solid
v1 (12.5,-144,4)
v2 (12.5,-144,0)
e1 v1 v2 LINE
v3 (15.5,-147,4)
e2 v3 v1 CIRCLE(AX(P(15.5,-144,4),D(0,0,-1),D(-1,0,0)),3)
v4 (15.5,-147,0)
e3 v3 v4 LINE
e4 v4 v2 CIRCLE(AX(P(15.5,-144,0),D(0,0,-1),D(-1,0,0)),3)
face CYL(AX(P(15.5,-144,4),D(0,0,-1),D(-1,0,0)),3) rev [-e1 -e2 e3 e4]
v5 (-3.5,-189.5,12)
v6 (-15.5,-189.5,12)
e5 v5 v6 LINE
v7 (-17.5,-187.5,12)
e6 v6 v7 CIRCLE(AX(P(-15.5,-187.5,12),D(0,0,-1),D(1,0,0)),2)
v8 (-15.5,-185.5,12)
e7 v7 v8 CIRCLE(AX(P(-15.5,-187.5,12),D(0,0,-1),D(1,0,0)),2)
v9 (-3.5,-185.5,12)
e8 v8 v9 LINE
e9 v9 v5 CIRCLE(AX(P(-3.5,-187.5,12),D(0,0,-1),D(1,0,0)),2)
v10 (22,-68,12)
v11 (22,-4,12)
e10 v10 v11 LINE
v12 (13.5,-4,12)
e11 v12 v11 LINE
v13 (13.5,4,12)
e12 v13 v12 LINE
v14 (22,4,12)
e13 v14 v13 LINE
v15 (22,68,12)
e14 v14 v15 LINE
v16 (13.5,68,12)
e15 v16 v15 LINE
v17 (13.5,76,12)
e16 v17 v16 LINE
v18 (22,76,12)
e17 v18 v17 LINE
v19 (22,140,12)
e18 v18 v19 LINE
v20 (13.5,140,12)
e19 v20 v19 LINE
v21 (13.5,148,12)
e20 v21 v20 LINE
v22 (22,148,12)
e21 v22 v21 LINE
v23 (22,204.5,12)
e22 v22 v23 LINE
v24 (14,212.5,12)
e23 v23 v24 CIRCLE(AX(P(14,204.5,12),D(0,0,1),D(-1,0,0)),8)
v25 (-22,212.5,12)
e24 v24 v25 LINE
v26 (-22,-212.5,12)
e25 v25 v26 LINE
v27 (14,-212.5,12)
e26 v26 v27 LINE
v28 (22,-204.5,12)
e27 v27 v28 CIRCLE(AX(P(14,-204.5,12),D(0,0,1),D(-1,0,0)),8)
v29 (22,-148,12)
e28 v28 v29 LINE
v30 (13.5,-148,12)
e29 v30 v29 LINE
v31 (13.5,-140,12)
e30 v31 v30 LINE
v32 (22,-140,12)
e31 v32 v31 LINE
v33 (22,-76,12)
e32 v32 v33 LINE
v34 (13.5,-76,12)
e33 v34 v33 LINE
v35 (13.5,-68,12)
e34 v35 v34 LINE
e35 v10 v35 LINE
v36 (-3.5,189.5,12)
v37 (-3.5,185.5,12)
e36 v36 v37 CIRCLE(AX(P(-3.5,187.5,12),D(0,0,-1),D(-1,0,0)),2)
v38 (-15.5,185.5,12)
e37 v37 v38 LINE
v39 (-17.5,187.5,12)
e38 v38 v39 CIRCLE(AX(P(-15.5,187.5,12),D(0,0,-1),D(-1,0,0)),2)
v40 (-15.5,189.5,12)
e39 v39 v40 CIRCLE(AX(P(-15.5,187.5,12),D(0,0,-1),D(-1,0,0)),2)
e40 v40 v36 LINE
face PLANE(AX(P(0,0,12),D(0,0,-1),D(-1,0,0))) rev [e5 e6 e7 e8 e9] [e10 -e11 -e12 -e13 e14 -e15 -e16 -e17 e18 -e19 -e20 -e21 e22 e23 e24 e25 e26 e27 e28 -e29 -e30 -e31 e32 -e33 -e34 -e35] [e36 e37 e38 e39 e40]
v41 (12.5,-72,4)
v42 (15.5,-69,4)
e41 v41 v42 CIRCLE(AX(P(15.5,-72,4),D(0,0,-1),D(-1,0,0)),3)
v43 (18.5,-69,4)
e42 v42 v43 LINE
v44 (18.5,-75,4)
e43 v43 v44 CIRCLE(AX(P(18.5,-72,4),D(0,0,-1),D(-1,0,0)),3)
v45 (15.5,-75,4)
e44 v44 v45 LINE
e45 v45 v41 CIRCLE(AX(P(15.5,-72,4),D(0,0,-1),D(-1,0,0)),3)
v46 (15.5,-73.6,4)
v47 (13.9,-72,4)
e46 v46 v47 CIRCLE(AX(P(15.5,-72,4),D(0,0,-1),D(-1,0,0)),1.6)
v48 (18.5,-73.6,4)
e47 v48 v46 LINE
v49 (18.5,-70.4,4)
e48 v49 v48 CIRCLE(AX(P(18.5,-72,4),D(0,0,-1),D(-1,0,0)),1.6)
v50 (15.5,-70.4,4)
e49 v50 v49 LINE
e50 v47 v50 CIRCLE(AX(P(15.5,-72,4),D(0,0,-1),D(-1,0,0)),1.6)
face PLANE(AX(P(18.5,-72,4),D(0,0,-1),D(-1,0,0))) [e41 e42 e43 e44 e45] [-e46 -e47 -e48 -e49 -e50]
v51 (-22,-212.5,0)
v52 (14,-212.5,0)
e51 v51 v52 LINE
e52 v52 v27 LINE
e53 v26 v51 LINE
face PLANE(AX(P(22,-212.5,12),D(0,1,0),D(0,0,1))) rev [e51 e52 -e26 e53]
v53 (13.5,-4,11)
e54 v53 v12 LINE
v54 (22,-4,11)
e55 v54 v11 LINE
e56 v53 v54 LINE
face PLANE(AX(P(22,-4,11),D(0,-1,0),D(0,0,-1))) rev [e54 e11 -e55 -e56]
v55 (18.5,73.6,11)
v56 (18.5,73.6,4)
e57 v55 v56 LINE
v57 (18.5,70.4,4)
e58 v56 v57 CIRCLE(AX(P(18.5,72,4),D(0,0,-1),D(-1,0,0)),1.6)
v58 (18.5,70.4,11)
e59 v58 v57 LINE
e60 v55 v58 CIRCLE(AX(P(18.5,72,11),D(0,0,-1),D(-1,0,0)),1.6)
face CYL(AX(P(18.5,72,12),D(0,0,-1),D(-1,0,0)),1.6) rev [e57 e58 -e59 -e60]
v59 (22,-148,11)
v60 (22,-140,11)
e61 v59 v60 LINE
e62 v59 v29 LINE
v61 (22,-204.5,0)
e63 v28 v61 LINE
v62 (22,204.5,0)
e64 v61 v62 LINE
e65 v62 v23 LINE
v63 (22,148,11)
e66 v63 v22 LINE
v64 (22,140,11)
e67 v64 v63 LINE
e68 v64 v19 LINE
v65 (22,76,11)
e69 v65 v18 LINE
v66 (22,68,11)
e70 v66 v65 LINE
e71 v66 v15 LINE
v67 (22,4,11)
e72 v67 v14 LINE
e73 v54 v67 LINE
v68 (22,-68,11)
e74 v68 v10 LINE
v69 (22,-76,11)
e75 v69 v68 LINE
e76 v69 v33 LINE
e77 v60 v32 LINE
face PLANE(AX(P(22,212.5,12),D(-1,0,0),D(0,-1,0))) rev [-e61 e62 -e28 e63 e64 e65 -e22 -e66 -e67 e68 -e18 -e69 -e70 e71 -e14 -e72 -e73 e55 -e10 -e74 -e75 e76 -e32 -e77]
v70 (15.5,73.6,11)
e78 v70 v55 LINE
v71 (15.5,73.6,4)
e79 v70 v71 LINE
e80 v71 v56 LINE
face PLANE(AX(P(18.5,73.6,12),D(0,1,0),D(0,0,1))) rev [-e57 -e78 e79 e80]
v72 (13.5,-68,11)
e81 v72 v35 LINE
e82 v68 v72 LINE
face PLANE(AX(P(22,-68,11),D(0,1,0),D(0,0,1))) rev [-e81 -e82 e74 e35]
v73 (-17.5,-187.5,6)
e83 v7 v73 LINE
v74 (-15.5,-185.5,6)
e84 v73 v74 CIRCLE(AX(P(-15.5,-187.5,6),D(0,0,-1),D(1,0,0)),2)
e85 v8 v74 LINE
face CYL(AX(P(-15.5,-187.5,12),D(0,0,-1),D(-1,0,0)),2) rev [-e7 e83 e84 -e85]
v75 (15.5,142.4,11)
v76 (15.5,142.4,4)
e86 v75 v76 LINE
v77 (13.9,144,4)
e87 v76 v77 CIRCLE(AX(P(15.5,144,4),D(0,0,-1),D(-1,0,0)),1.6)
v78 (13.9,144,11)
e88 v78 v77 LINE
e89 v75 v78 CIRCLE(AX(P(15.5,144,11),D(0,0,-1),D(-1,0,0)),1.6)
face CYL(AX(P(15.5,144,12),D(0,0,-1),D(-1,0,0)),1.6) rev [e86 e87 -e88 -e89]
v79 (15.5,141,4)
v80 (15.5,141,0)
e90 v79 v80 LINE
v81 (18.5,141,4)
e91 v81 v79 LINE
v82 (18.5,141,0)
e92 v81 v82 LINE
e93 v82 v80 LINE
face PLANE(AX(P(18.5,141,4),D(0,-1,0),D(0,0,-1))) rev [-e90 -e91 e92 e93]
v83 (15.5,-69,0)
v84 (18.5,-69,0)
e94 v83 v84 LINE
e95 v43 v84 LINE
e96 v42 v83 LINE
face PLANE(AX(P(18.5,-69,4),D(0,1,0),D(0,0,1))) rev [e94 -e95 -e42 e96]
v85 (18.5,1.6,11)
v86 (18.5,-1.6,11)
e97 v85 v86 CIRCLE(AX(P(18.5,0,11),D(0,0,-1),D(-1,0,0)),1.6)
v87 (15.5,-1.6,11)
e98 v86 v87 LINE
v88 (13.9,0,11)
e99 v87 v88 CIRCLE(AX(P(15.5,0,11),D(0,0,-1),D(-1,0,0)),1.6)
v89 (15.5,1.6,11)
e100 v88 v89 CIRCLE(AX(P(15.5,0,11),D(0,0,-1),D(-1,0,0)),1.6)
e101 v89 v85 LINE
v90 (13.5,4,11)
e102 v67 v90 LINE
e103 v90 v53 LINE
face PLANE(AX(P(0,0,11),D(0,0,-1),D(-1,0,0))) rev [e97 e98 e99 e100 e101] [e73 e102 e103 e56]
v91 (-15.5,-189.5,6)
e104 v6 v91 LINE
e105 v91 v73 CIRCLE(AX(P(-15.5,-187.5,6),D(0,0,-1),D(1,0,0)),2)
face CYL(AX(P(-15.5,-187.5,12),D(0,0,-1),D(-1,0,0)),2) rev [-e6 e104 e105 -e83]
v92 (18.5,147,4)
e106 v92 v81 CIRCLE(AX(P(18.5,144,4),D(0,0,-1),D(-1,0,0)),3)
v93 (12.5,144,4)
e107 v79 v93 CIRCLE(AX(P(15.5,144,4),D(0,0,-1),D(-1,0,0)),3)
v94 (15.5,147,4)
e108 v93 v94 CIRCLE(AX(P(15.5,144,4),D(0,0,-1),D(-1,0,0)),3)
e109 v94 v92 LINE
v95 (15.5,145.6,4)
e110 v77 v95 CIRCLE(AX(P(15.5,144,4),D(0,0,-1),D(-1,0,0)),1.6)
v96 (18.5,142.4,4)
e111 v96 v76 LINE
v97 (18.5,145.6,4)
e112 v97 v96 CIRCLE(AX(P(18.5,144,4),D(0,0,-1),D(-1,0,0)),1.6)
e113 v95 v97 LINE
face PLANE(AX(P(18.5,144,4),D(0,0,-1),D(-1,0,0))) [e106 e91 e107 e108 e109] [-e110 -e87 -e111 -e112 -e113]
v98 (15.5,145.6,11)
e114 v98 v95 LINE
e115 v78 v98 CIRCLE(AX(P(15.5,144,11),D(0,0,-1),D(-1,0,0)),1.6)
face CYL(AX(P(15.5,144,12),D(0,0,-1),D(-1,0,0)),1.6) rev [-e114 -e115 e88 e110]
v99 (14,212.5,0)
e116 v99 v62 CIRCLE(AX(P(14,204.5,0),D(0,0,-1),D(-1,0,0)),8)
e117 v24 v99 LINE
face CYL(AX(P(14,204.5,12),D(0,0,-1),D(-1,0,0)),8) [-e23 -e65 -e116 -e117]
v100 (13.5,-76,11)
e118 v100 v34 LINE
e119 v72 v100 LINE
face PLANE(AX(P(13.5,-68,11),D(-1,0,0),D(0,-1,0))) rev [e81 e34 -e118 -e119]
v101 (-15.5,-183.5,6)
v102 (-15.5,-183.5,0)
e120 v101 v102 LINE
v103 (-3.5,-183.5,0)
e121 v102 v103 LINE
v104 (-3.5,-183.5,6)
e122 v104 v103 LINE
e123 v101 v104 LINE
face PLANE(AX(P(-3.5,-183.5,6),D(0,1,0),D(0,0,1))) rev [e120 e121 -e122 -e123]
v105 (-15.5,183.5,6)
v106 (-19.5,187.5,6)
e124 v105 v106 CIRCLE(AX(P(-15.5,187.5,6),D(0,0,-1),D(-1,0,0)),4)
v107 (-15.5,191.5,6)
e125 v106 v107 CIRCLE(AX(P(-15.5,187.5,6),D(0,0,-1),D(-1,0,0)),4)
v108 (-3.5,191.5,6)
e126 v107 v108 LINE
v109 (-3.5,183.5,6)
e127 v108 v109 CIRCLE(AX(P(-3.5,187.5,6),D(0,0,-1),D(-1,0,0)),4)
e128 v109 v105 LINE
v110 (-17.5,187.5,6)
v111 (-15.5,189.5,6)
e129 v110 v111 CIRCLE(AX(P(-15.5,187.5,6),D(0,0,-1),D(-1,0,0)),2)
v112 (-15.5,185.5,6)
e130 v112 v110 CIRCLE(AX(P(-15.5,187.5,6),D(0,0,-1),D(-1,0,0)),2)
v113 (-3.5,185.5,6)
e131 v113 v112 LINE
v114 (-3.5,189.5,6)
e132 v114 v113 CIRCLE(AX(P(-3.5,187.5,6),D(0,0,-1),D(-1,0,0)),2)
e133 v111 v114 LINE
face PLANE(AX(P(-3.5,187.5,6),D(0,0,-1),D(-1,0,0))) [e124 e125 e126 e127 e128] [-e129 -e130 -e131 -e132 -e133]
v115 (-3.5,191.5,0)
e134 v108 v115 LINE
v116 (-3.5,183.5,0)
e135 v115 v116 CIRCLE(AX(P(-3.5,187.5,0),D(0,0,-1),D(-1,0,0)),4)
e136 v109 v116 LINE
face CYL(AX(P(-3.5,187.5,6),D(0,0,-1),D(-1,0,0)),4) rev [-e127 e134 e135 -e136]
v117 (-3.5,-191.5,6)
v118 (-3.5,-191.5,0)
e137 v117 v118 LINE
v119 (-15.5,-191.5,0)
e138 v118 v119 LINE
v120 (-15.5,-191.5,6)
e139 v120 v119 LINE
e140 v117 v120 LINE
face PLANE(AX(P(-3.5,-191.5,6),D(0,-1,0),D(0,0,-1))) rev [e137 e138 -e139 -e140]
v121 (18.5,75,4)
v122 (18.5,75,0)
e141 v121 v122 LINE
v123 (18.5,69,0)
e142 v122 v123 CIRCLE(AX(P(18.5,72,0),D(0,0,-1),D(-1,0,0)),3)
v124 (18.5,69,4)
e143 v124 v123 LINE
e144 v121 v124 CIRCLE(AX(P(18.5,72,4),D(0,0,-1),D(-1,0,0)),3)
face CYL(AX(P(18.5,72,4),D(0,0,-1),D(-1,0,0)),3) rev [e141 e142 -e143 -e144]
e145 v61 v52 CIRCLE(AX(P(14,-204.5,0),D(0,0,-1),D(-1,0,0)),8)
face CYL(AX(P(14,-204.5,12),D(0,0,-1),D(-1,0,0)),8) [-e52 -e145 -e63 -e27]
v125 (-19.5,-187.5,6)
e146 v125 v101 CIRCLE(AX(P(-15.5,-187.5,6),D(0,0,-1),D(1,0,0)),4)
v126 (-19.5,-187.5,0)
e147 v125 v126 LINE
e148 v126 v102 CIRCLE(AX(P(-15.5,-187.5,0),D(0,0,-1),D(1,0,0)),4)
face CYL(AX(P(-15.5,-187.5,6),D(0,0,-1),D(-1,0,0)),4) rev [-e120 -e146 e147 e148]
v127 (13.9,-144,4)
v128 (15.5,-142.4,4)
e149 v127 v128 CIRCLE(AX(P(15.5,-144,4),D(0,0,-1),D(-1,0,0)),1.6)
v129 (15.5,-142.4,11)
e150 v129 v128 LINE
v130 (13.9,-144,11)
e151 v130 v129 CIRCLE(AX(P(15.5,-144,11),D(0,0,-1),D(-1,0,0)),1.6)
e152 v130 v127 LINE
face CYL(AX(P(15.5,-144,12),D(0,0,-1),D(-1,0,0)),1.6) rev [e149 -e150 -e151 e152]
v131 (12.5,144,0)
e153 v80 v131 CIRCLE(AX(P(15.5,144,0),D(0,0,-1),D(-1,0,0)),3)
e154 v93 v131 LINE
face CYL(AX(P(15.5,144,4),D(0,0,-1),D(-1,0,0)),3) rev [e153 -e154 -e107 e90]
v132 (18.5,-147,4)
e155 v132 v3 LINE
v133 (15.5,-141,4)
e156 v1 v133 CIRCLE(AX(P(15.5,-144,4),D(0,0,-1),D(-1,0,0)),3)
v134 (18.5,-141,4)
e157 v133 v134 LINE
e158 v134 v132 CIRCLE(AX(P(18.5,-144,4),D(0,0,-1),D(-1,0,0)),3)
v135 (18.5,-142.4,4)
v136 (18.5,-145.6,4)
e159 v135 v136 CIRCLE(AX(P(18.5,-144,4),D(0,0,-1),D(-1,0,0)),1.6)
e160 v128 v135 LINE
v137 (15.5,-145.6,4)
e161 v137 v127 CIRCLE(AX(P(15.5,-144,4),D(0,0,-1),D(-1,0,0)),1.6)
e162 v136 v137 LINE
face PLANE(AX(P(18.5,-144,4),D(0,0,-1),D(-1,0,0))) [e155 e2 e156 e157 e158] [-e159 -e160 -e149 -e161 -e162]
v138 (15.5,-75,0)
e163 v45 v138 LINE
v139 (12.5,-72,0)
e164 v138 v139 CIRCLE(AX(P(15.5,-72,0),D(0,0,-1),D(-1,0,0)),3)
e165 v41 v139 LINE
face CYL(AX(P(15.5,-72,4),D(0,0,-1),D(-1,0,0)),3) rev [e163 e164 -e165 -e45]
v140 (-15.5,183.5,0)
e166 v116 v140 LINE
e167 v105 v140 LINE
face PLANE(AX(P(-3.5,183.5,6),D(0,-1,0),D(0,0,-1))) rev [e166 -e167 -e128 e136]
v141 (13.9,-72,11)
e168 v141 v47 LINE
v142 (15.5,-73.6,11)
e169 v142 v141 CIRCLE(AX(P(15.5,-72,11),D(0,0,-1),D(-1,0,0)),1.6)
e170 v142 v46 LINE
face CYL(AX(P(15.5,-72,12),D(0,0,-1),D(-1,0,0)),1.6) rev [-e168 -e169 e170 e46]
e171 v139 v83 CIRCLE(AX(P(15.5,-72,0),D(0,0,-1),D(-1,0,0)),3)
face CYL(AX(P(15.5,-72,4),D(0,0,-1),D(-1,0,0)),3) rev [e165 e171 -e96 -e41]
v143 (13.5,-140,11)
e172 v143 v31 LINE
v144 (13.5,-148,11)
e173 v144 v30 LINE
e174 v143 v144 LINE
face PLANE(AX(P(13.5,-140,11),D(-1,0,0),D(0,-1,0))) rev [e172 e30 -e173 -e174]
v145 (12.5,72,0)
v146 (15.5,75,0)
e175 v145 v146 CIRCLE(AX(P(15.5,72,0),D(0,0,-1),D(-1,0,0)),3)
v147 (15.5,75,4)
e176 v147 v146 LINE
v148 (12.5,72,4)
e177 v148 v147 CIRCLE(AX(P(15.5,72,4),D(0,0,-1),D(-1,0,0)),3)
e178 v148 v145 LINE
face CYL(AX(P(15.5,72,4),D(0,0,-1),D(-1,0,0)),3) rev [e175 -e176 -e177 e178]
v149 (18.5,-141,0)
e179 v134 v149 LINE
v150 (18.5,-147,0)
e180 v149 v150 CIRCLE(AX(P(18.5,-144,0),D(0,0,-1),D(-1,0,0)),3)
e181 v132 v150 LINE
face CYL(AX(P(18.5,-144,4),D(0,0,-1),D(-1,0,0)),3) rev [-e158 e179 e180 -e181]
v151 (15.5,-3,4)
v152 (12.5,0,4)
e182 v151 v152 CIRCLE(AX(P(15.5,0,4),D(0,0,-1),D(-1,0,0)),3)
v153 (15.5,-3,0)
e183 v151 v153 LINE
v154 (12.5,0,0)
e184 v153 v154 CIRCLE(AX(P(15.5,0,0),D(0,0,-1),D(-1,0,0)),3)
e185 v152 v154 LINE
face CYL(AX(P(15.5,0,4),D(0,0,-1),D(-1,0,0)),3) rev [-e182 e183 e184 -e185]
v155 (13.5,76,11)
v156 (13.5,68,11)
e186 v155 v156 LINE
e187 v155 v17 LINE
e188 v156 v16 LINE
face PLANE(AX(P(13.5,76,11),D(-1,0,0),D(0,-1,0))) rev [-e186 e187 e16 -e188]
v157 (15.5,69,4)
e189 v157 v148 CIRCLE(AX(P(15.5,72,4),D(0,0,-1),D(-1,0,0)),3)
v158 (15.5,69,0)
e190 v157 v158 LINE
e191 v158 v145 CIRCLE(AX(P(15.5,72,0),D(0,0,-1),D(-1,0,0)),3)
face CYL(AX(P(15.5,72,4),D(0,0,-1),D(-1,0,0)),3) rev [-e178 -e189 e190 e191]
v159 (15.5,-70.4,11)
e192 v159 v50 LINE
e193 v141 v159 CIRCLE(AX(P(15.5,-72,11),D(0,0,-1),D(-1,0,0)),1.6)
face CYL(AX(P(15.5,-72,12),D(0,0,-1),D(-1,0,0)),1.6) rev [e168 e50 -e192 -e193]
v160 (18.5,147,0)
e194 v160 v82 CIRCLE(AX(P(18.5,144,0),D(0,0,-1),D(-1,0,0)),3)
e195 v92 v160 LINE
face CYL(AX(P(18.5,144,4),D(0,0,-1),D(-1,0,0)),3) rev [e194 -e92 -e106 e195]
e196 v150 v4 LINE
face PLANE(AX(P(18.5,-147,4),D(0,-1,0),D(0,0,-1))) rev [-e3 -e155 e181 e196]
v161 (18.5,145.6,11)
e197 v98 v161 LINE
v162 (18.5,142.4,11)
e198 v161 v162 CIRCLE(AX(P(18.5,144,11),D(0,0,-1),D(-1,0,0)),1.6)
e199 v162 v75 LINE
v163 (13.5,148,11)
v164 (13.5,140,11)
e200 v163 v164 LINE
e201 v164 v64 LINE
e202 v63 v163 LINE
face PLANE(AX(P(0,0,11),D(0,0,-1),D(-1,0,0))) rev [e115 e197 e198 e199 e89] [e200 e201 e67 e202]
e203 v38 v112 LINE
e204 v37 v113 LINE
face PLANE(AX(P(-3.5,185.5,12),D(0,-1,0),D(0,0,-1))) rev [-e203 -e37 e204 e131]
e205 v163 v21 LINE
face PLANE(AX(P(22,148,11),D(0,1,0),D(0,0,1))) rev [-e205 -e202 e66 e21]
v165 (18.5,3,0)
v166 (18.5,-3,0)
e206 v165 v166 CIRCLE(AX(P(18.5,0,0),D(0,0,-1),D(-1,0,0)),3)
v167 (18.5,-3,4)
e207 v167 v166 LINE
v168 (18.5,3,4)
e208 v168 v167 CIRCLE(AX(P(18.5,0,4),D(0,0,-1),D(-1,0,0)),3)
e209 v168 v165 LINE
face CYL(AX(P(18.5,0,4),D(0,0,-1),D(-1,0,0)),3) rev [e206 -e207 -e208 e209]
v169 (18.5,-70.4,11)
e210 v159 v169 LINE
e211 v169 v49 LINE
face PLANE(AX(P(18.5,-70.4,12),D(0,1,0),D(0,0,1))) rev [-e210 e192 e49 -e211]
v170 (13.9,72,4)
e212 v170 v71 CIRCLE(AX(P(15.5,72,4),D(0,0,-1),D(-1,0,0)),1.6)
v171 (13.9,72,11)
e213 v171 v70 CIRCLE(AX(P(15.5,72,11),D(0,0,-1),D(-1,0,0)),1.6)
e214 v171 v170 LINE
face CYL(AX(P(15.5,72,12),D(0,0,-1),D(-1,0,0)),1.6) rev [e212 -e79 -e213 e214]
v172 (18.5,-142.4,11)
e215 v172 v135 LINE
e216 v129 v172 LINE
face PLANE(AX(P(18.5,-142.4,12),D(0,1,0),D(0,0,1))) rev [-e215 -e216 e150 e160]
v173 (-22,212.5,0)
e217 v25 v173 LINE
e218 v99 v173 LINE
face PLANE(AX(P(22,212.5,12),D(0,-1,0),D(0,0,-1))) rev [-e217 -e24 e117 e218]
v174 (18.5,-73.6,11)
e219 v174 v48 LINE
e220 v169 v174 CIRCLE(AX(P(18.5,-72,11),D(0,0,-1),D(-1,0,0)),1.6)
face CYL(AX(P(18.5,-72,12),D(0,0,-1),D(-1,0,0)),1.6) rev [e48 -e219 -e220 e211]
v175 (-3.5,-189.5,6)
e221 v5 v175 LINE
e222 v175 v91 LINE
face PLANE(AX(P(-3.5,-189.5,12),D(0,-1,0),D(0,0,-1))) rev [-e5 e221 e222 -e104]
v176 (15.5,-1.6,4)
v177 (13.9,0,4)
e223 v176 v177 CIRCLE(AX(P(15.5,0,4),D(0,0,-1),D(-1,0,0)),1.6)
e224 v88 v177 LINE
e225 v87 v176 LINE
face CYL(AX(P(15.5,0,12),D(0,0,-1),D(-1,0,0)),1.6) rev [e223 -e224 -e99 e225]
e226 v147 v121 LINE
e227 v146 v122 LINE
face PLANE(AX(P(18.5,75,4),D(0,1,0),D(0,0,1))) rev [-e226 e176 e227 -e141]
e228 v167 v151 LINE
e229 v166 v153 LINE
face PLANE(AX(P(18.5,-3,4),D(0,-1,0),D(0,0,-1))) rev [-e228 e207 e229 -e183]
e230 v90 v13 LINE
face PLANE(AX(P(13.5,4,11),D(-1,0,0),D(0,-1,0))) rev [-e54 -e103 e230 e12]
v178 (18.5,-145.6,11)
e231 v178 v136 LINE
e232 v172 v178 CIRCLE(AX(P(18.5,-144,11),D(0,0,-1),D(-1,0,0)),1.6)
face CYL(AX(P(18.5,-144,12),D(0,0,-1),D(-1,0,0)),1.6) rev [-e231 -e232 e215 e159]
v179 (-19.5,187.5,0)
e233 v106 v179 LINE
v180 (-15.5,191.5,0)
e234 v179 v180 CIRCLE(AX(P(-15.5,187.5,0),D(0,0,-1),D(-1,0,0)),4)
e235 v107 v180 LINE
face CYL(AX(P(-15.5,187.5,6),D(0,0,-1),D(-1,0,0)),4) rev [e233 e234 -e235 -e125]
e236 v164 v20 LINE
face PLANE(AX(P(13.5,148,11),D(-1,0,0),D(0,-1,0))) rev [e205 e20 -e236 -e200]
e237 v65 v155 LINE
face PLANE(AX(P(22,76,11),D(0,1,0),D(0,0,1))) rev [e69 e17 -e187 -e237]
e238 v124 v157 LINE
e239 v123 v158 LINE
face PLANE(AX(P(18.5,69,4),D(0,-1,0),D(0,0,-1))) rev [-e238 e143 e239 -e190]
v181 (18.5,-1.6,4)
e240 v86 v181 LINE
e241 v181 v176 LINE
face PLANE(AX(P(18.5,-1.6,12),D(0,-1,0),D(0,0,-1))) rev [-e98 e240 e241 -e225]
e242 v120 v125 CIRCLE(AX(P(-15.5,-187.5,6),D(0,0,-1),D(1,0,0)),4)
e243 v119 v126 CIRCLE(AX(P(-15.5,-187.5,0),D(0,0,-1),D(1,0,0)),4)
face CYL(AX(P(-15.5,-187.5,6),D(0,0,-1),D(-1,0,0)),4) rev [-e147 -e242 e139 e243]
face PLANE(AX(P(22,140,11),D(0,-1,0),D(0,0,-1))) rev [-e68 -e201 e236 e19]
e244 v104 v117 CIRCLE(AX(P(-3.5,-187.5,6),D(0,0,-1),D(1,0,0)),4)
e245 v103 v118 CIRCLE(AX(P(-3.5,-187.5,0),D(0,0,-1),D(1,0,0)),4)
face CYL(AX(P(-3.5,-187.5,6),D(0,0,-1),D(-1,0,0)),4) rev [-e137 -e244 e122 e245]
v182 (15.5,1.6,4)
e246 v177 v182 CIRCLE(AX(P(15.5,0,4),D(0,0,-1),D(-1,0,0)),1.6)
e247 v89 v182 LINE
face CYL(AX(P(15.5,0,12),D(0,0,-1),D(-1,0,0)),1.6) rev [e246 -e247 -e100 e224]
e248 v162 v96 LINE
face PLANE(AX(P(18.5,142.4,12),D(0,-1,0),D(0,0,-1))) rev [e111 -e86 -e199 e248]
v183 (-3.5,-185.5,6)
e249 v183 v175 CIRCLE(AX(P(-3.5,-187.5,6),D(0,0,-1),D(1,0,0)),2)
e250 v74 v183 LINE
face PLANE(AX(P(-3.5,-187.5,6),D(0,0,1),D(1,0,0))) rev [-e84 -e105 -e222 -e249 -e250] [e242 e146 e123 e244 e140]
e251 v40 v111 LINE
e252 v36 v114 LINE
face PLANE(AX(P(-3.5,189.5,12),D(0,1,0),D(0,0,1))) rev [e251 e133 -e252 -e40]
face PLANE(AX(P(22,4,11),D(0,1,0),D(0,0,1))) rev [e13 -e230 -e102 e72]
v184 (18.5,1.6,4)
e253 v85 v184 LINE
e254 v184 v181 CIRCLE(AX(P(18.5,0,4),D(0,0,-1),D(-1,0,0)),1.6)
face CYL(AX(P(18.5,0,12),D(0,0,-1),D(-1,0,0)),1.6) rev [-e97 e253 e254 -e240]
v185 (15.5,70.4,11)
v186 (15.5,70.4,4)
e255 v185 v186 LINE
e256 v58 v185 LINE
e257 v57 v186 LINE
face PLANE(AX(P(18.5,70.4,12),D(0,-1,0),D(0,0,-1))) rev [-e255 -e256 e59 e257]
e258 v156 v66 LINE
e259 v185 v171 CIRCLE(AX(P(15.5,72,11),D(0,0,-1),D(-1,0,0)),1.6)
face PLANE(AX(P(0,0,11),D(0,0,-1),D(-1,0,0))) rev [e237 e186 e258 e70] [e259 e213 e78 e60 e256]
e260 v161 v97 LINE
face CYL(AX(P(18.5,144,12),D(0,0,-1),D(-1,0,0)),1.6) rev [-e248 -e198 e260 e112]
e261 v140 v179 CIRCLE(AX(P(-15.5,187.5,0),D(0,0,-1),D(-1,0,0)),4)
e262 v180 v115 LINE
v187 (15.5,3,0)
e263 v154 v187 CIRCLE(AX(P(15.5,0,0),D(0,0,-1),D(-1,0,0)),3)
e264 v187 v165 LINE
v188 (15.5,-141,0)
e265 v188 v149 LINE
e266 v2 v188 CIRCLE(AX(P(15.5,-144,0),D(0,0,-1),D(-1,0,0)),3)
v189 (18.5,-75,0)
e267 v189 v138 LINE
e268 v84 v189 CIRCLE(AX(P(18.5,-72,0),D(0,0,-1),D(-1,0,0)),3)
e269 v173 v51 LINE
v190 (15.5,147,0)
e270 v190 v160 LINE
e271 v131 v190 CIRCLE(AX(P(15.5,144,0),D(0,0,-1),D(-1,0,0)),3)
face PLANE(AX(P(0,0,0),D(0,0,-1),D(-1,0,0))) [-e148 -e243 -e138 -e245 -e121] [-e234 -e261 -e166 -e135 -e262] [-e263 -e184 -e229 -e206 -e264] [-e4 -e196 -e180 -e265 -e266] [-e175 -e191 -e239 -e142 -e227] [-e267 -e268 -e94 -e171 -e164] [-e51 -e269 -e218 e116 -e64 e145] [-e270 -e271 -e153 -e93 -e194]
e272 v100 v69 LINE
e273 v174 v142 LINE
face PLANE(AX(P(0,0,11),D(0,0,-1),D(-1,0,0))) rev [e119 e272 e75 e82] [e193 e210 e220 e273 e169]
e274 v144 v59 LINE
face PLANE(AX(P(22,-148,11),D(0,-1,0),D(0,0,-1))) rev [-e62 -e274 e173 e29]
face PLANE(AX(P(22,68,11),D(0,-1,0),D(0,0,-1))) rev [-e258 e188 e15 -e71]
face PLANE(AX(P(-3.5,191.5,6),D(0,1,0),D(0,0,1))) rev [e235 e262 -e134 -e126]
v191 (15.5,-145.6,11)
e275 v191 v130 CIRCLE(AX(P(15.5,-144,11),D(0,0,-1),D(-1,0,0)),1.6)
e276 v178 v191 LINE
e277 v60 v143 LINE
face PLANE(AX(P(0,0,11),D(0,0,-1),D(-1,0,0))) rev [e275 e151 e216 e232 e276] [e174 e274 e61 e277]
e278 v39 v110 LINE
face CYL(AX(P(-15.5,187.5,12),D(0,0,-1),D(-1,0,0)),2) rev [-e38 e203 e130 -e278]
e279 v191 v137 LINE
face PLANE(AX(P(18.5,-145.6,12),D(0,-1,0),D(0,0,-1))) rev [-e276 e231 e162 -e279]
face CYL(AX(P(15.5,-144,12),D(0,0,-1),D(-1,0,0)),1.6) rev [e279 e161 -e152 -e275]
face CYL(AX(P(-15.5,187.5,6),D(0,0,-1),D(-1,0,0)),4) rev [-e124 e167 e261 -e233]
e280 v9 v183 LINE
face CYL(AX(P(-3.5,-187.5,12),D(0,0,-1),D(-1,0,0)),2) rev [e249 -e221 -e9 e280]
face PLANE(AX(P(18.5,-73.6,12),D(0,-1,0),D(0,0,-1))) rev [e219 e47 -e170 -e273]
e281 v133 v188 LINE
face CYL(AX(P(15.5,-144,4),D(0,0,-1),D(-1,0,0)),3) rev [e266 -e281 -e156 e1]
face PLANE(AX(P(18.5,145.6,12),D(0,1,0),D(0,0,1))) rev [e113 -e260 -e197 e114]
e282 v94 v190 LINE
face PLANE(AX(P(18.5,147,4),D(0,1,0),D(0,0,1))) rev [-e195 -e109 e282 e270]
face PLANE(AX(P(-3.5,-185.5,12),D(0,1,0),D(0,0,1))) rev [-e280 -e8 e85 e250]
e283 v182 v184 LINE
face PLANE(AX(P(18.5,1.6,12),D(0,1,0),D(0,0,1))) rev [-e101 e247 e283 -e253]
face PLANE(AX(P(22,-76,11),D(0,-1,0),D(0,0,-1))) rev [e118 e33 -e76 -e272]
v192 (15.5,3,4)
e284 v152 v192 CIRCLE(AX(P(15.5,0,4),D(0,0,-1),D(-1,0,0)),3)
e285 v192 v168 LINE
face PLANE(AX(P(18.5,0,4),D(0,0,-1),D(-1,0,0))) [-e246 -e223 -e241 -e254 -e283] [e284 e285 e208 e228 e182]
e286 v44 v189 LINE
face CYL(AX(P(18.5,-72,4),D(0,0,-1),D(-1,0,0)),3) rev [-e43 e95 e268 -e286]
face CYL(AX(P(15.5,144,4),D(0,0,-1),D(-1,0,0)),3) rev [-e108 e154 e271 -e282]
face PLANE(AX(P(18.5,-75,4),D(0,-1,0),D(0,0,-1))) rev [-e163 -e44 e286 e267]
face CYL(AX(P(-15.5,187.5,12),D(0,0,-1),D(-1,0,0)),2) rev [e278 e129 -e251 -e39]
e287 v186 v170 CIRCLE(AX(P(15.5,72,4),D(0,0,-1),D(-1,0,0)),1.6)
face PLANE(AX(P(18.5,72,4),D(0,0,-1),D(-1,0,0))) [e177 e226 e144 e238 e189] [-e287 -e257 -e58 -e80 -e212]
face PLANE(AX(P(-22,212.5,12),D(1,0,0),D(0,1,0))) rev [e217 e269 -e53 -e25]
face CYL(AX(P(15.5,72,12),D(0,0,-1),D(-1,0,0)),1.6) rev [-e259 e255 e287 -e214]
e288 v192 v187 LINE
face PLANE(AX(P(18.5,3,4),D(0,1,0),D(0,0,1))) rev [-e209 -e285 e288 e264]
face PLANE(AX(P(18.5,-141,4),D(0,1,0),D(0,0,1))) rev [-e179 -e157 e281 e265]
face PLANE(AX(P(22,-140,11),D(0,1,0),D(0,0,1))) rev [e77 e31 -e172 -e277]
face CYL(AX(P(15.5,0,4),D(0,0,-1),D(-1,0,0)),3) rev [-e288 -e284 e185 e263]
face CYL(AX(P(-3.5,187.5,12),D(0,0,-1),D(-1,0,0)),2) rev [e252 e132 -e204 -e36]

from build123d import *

# Parameters (mm, degrees)
SKETCH_1_W             = 44
SKETCH_1_H             = 425
EXTRUDE_1_DEPTH        = 12
FILLET_1_R             = 8
CUT_EXTRUDE_1_DEPTH    = 6
CUT_EXTRUDE_2_DEPTH    = 214.720027138
SKETCH_6_W             = 8.5
SKETCH_6_H             = 8
CUT_EXTRUDE_4_DEPTH    = 1
CUT_EXTRUDE_5_DEPTH    = 4
CUT_EXTRUDE_6_DEPTH    = 214.785523364
PATTERN_LINEAR_1_COUNT = 5
PATTERN_LINEAR_1_PITCH = 72


with BuildPart() as part:
    # 草图1 → 凸台-拉伸1 (new body)
    with BuildSketch(Plane.XY):
        Rectangle(SKETCH_1_W, SKETCH_1_H)
    extrude(amount=EXTRUDE_1_DEPTH)

    # 圆角1
    fillet_1_edges = [part.edges().sort_by_distance(p)[0] for p in [
        (22, 212.5, 6),
        (22, -212.5, 6),
    ]]
    fillet(fillet_1_edges, radius=FILLET_1_R)

    # 草图3 → 切除-拉伸1 (cut)
    with BuildSketch(Plane(origin=(0, 0, 0), x_dir=(-1, 0, 0), z_dir=(0, 0, -1))):
        with BuildLine():
            Line((3.5, 191.5), (15.5, 191.5))
            ThreePointArc((15.5, 191.5), (19.5, 187.5), (15.5, 183.5))
            Line((15.5, 183.5), (3.5, 183.5))
            ThreePointArc((3.5, 183.5), (-0.5, 187.5), (3.5, 191.5))
        make_face()
        with BuildLine():
            Line((3.5, -191.5), (15.5, -191.5))
            ThreePointArc((15.5, -191.5), (19.5, -187.5), (15.5, -183.5))
            Line((15.5, -183.5), (3.5, -183.5))
            ThreePointArc((3.5, -183.5), (-0.5, -187.5), (3.5, -191.5))
        make_face()
    extrude(amount=-CUT_EXTRUDE_1_DEPTH, mode=Mode.SUBTRACT)

    # 草图4 → 切除-拉伸2 (cut, through all)
    with BuildSketch(Plane(origin=(0, 0, 6), x_dir=(-1, 0, 0), z_dir=(0, 0, -1))):
        with BuildLine():
            Line((3.5, 189.5), (15.5, 189.5))
            ThreePointArc((15.5, 189.5), (17.5, 187.5), (15.5, 185.5))
            Line((15.5, 185.5), (3.5, 185.5))
            ThreePointArc((3.5, 185.5), (1.5, 187.5), (3.5, 189.5))
        make_face()
        with BuildLine():
            Line((3.5, -189.5), (15.5, -189.5))
            ThreePointArc((15.5, -189.5), (17.5, -187.5), (15.5, -185.5))
            Line((15.5, -185.5), (3.5, -185.5))
            ThreePointArc((3.5, -185.5), (1.5, -187.5), (3.5, -189.5))
        make_face()
    extrude(amount=-CUT_EXTRUDE_2_DEPTH, mode=Mode.SUBTRACT)

    # 草图6 → 切除-拉伸4 (cut)
    with BuildSketch(Plane.XY.offset(12)):
        with Locations((17.75, 144)):
            Rectangle(SKETCH_6_W, SKETCH_6_H)
        with Locations((17.75, 72)):
            Rectangle(SKETCH_6_W, SKETCH_6_H)
        with Locations((17.75, 0)):
            Rectangle(SKETCH_6_W, SKETCH_6_H)
        with Locations((17.75, -72)):
            Rectangle(SKETCH_6_W, SKETCH_6_H)
        with Locations((17.75, -144)):
            Rectangle(SKETCH_6_W, SKETCH_6_H)
    extrude(amount=-CUT_EXTRUDE_4_DEPTH, mode=Mode.SUBTRACT)

    # 草图7 → 切除-拉伸5 (cut)
    with BuildSketch(Plane(origin=(0, 0, 0), x_dir=(-1, 0, 0), z_dir=(0, 0, -1))):
        with BuildLine():
            Line((-18.5, 147), (-15.5, 147))
            ThreePointArc((-15.5, 147), (-12.5, 144), (-15.5, 141))
            Line((-15.5, 141), (-18.5, 141))
            ThreePointArc((-18.5, 141), (-21.5, 144), (-18.5, 147))
        make_face()
    cut_extrude_5 = extrude(amount=-CUT_EXTRUDE_5_DEPTH, mode=Mode.SUBTRACT)

    # 草图8 → 切除-拉伸6 (cut, through all)
    with BuildSketch(Plane(origin=(0, 0, 4), x_dir=(-1, 0, 0), z_dir=(0, 0, -1))):
        with BuildLine():
            Line((-18.5, 145.6), (-15.5, 145.6))
            ThreePointArc((-15.5, 145.6), (-13.9, 144), (-15.5, 142.4))
            Line((-15.5, 142.4), (-18.5, 142.4))
            ThreePointArc((-18.5, 142.4), (-20.1, 144), (-18.5, 145.6))
        make_face()
    cut_extrude_6 = extrude(amount=-CUT_EXTRUDE_6_DEPTH, mode=Mode.SUBTRACT)

    # 阵列(线性)1: 切除-拉伸5, 切除-拉伸6 ×5
    with Locations(*[(0, -i * PATTERN_LINEAR_1_PITCH, 0) for i in range(1, PATTERN_LINEAR_1_COUNT)]):
        add(cut_extrude_5, mode=Mode.SUBTRACT)
        add(cut_extrude_6, mode=Mode.SUBTRACT)


solid = part.part
